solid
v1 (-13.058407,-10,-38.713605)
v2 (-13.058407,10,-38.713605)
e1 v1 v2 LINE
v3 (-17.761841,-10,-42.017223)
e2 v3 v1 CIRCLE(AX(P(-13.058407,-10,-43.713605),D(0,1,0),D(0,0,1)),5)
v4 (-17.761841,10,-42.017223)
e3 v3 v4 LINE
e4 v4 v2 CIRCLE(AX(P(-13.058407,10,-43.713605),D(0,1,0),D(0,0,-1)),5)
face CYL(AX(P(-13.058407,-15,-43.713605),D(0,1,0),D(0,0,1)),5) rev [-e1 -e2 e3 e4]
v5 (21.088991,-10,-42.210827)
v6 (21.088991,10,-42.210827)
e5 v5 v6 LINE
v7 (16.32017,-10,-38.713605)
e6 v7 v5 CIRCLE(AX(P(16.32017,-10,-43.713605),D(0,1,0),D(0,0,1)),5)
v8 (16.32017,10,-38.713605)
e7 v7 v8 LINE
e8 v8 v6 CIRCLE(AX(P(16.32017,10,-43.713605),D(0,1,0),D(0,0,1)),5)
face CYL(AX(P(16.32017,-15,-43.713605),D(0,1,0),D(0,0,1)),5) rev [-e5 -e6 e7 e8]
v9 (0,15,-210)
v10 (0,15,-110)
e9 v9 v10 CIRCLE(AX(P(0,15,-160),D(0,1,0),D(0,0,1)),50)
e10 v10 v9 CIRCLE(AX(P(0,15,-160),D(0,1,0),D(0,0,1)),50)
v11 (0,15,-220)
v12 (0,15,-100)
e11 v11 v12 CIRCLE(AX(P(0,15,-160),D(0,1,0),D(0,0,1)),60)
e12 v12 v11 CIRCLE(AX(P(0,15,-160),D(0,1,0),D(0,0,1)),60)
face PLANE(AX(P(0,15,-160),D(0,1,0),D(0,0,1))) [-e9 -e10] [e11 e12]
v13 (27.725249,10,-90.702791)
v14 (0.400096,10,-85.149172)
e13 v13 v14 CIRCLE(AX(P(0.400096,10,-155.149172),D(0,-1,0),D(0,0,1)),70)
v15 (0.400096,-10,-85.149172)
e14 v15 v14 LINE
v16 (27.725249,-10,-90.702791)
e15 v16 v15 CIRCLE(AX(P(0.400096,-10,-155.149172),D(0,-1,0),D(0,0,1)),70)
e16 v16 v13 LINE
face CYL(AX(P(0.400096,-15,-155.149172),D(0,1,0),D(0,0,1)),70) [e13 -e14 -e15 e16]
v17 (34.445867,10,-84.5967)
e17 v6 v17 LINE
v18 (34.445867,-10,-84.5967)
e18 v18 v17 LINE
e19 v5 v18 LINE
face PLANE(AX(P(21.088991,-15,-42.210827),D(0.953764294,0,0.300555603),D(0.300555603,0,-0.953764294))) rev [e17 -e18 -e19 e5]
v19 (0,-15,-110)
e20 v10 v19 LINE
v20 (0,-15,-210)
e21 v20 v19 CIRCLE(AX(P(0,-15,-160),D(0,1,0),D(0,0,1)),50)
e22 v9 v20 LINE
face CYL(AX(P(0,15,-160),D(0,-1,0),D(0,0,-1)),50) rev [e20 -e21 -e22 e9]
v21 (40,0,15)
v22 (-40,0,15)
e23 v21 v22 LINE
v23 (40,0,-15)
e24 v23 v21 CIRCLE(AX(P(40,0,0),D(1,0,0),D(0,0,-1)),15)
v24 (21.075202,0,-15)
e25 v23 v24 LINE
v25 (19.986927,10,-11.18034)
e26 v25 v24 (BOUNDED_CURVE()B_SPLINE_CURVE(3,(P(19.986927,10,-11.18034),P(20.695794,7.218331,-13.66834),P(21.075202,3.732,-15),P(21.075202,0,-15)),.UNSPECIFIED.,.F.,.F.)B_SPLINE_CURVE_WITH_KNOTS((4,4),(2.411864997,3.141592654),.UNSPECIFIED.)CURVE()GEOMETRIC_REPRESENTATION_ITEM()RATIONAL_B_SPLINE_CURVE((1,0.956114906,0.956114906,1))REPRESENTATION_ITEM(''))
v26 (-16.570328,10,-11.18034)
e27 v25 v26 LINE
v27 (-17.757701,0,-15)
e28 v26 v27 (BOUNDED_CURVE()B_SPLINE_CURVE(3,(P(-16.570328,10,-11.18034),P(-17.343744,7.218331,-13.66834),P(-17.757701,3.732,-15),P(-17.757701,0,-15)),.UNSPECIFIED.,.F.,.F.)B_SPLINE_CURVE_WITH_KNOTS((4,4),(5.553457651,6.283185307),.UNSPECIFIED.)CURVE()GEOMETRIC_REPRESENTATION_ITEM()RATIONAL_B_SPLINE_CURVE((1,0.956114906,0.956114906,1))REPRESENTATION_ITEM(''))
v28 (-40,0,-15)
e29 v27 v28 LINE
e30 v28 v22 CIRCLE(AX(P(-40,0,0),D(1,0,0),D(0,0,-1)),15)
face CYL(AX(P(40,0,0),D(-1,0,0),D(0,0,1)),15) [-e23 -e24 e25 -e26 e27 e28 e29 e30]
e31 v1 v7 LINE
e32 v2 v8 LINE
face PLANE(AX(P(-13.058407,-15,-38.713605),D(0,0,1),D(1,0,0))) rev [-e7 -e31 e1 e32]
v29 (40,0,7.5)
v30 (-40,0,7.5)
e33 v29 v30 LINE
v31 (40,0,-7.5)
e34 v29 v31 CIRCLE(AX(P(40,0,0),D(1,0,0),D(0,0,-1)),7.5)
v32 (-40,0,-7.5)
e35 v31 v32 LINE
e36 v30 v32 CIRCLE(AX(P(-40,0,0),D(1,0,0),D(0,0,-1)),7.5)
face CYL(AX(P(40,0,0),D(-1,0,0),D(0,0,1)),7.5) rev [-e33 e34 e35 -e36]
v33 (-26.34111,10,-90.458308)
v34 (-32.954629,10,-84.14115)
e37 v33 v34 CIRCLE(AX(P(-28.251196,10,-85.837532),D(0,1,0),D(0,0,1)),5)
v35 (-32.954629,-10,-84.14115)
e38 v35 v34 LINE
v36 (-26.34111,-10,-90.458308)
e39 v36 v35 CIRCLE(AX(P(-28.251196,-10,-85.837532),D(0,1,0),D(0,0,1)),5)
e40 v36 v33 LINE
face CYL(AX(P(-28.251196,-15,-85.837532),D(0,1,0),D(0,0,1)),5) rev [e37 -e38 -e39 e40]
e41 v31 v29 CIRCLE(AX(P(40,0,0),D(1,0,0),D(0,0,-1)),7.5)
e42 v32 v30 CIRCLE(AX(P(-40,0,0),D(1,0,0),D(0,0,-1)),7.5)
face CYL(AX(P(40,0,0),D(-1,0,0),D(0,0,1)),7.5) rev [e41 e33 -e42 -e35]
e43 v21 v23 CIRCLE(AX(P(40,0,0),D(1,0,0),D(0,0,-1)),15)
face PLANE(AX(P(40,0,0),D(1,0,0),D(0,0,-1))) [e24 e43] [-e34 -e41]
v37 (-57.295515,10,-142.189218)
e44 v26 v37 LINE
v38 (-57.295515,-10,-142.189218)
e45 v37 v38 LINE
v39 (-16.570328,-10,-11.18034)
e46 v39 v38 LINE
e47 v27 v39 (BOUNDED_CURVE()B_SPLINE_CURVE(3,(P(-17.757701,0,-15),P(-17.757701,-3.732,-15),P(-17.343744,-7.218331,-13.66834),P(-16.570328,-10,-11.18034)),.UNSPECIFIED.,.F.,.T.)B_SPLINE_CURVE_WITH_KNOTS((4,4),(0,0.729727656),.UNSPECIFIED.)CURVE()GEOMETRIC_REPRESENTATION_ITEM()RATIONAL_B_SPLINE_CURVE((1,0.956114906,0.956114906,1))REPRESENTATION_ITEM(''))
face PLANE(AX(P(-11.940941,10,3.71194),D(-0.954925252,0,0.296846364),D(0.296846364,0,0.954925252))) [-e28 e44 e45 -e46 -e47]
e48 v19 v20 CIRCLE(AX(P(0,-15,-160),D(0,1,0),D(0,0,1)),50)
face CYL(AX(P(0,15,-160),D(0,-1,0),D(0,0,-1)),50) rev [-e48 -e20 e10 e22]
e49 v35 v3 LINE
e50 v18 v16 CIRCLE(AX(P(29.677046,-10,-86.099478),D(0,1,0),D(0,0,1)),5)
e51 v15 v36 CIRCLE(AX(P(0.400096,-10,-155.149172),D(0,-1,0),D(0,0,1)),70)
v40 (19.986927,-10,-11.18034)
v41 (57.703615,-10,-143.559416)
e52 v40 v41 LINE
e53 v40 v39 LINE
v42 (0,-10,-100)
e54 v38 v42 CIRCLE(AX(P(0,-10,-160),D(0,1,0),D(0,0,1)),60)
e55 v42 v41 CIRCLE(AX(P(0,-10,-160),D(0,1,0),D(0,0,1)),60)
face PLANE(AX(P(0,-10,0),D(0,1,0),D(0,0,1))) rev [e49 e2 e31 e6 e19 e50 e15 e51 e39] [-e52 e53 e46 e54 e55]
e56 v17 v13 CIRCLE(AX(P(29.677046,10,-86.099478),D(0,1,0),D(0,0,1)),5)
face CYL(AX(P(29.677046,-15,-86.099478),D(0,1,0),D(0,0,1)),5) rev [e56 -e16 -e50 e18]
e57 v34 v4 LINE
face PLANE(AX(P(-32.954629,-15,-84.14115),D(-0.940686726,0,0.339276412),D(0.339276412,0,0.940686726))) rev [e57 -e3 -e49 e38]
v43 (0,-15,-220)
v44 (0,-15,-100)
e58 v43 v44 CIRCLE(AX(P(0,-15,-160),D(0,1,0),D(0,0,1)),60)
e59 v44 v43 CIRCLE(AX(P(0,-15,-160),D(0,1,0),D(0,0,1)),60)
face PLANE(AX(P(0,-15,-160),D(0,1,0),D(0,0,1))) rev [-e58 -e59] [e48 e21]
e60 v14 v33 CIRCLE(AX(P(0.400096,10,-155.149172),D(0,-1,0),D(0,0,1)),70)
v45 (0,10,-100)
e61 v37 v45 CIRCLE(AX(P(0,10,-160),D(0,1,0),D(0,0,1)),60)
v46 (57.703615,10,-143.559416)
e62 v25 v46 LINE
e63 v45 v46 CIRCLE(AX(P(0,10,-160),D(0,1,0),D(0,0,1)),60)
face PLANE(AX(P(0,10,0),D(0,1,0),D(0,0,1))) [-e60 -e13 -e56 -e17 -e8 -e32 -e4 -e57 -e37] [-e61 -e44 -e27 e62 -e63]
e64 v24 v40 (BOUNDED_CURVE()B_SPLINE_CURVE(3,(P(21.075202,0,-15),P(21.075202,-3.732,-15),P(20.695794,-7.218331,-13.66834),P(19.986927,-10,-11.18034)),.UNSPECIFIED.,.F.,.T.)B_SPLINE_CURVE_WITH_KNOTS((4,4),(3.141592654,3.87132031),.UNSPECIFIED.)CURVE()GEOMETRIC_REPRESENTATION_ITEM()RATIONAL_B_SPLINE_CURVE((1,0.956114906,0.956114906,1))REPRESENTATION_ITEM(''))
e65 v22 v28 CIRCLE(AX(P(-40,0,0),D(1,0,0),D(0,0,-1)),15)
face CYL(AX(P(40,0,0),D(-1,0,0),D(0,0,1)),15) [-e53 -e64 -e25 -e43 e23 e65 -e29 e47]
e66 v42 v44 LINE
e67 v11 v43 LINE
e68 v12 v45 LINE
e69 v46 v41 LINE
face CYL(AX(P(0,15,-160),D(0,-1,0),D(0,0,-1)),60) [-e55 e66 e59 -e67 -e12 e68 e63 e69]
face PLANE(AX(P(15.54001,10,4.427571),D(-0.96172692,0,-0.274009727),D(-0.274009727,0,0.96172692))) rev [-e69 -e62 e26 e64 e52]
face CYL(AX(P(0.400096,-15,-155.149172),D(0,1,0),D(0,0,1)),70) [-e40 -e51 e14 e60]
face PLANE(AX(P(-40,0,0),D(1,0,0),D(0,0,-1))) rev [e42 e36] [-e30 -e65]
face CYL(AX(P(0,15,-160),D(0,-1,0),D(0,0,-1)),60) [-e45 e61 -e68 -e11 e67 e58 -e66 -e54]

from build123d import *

# Parameters (mm, degrees)
PIVOT_TUBE_SKETCH_R         = 15
PIVOT_TUBE_SKETCH_R_2       = 7.5
PIVOT_TUBE_30X_15_DEPTH     = 40
ARM_WEB_20MM_DEPTH          = 10
RING_HUB_SKETCH_R           = 60
RING_HUB_SKETCH_R_2         = 50
RING_HUB_120X_100_DEPTH     = 15
ARM_LIGHTENING_POCKET_DEPTH = 230.401394939


with BuildPart() as part:
    # Pivot Tube Sketch → Pivot Tube Ø30xØ15 (new, symmetric)
    with BuildSketch(Plane(origin=(0, 0, 0), x_dir=(0, 0, -1), z_dir=(1, 0, 0))):
        Circle(PIVOT_TUBE_SKETCH_R)
        Circle(PIVOT_TUBE_SKETCH_R_2, mode=Mode.SUBTRACT)
    extrude(amount=PIVOT_TUBE_30X_15_DEPTH, both=True)

    # Arm Web Sketch → Arm Web 20mm (add, symmetric)
    with BuildSketch(Plane(origin=(0, 0, 0), x_dir=(1, 0, 0), z_dir=(0, 1, 0))):
        with BuildLine():
            Line((-57.295515099, 142.189218166), (-16.443257741, 10.771566203))
            Line((-16.443257741, 10.771566203), (19.870461321, 10.771566203))
            Line((19.870461321, 10.771566203), (57.703615224, 143.559416372))
            ThreePointArc((57.703615224, 143.559416372), (0.714840688, 100.004258461), (-57.295515099, 142.189218166))
        make_face()
    extrude(amount=ARM_WEB_20MM_DEPTH, both=True)

    # Ring Hub Sketch → Ring Hub Ø120xØ100 (add, symmetric)
    with BuildSketch(Plane(origin=(0, 0, 0), x_dir=(1, 0, 0), z_dir=(0, 1, 0))):
        with Locations(Location((0, 160, 0), (0, 0, 270))):
            Circle(RING_HUB_SKETCH_R)
        with Locations(Location((0, 160, 0), (0, 0, 270))):
            Circle(RING_HUB_SKETCH_R_2, mode=Mode.SUBTRACT)
    extrude(amount=RING_HUB_120X_100_DEPTH, both=True)

    # Arm Pocket Sketch → Arm Lightening Pocket (cut, through all)
    with BuildSketch(Plane(origin=(0, 10, 0), x_dir=(1, 0, 0), z_dir=(0, 1, 0))):
        with BuildLine():
            Line((-13.0584069, 38.71360492), (16.320169694, 38.71360492))
            ThreePointArc((16.320169694, 38.71360492), (19.277035427, 39.681614712), (21.088991166, 42.210826904))
            Line((21.088991166, 42.210826904), (34.445867452, 84.596700091))
            ThreePointArc((34.445867452, 84.596700091), (33.039335954, 89.800154549), (27.725249342, 90.702791032))
            ThreePointArc((27.725249342, 90.702791032), (0.71662682, 85.149887641), (-26.34110962, 90.458307872))
            ThreePointArc((-26.34110962, 90.458307872), (-31.704790858, 89.453148124), (-32.954629394, 84.141149802))
            Line((-32.954629394, 84.141149802), (-17.761840528, 42.017222858))
            ThreePointArc((-17.761840528, 42.017222858), (-15.932262297, 39.622033687), (-13.0584069, 38.71360492))
        make_face()
    extrude(amount=-ARM_LIGHTENING_POCKET_DEPTH, mode=Mode.SUBTRACT)


solid = part.part
